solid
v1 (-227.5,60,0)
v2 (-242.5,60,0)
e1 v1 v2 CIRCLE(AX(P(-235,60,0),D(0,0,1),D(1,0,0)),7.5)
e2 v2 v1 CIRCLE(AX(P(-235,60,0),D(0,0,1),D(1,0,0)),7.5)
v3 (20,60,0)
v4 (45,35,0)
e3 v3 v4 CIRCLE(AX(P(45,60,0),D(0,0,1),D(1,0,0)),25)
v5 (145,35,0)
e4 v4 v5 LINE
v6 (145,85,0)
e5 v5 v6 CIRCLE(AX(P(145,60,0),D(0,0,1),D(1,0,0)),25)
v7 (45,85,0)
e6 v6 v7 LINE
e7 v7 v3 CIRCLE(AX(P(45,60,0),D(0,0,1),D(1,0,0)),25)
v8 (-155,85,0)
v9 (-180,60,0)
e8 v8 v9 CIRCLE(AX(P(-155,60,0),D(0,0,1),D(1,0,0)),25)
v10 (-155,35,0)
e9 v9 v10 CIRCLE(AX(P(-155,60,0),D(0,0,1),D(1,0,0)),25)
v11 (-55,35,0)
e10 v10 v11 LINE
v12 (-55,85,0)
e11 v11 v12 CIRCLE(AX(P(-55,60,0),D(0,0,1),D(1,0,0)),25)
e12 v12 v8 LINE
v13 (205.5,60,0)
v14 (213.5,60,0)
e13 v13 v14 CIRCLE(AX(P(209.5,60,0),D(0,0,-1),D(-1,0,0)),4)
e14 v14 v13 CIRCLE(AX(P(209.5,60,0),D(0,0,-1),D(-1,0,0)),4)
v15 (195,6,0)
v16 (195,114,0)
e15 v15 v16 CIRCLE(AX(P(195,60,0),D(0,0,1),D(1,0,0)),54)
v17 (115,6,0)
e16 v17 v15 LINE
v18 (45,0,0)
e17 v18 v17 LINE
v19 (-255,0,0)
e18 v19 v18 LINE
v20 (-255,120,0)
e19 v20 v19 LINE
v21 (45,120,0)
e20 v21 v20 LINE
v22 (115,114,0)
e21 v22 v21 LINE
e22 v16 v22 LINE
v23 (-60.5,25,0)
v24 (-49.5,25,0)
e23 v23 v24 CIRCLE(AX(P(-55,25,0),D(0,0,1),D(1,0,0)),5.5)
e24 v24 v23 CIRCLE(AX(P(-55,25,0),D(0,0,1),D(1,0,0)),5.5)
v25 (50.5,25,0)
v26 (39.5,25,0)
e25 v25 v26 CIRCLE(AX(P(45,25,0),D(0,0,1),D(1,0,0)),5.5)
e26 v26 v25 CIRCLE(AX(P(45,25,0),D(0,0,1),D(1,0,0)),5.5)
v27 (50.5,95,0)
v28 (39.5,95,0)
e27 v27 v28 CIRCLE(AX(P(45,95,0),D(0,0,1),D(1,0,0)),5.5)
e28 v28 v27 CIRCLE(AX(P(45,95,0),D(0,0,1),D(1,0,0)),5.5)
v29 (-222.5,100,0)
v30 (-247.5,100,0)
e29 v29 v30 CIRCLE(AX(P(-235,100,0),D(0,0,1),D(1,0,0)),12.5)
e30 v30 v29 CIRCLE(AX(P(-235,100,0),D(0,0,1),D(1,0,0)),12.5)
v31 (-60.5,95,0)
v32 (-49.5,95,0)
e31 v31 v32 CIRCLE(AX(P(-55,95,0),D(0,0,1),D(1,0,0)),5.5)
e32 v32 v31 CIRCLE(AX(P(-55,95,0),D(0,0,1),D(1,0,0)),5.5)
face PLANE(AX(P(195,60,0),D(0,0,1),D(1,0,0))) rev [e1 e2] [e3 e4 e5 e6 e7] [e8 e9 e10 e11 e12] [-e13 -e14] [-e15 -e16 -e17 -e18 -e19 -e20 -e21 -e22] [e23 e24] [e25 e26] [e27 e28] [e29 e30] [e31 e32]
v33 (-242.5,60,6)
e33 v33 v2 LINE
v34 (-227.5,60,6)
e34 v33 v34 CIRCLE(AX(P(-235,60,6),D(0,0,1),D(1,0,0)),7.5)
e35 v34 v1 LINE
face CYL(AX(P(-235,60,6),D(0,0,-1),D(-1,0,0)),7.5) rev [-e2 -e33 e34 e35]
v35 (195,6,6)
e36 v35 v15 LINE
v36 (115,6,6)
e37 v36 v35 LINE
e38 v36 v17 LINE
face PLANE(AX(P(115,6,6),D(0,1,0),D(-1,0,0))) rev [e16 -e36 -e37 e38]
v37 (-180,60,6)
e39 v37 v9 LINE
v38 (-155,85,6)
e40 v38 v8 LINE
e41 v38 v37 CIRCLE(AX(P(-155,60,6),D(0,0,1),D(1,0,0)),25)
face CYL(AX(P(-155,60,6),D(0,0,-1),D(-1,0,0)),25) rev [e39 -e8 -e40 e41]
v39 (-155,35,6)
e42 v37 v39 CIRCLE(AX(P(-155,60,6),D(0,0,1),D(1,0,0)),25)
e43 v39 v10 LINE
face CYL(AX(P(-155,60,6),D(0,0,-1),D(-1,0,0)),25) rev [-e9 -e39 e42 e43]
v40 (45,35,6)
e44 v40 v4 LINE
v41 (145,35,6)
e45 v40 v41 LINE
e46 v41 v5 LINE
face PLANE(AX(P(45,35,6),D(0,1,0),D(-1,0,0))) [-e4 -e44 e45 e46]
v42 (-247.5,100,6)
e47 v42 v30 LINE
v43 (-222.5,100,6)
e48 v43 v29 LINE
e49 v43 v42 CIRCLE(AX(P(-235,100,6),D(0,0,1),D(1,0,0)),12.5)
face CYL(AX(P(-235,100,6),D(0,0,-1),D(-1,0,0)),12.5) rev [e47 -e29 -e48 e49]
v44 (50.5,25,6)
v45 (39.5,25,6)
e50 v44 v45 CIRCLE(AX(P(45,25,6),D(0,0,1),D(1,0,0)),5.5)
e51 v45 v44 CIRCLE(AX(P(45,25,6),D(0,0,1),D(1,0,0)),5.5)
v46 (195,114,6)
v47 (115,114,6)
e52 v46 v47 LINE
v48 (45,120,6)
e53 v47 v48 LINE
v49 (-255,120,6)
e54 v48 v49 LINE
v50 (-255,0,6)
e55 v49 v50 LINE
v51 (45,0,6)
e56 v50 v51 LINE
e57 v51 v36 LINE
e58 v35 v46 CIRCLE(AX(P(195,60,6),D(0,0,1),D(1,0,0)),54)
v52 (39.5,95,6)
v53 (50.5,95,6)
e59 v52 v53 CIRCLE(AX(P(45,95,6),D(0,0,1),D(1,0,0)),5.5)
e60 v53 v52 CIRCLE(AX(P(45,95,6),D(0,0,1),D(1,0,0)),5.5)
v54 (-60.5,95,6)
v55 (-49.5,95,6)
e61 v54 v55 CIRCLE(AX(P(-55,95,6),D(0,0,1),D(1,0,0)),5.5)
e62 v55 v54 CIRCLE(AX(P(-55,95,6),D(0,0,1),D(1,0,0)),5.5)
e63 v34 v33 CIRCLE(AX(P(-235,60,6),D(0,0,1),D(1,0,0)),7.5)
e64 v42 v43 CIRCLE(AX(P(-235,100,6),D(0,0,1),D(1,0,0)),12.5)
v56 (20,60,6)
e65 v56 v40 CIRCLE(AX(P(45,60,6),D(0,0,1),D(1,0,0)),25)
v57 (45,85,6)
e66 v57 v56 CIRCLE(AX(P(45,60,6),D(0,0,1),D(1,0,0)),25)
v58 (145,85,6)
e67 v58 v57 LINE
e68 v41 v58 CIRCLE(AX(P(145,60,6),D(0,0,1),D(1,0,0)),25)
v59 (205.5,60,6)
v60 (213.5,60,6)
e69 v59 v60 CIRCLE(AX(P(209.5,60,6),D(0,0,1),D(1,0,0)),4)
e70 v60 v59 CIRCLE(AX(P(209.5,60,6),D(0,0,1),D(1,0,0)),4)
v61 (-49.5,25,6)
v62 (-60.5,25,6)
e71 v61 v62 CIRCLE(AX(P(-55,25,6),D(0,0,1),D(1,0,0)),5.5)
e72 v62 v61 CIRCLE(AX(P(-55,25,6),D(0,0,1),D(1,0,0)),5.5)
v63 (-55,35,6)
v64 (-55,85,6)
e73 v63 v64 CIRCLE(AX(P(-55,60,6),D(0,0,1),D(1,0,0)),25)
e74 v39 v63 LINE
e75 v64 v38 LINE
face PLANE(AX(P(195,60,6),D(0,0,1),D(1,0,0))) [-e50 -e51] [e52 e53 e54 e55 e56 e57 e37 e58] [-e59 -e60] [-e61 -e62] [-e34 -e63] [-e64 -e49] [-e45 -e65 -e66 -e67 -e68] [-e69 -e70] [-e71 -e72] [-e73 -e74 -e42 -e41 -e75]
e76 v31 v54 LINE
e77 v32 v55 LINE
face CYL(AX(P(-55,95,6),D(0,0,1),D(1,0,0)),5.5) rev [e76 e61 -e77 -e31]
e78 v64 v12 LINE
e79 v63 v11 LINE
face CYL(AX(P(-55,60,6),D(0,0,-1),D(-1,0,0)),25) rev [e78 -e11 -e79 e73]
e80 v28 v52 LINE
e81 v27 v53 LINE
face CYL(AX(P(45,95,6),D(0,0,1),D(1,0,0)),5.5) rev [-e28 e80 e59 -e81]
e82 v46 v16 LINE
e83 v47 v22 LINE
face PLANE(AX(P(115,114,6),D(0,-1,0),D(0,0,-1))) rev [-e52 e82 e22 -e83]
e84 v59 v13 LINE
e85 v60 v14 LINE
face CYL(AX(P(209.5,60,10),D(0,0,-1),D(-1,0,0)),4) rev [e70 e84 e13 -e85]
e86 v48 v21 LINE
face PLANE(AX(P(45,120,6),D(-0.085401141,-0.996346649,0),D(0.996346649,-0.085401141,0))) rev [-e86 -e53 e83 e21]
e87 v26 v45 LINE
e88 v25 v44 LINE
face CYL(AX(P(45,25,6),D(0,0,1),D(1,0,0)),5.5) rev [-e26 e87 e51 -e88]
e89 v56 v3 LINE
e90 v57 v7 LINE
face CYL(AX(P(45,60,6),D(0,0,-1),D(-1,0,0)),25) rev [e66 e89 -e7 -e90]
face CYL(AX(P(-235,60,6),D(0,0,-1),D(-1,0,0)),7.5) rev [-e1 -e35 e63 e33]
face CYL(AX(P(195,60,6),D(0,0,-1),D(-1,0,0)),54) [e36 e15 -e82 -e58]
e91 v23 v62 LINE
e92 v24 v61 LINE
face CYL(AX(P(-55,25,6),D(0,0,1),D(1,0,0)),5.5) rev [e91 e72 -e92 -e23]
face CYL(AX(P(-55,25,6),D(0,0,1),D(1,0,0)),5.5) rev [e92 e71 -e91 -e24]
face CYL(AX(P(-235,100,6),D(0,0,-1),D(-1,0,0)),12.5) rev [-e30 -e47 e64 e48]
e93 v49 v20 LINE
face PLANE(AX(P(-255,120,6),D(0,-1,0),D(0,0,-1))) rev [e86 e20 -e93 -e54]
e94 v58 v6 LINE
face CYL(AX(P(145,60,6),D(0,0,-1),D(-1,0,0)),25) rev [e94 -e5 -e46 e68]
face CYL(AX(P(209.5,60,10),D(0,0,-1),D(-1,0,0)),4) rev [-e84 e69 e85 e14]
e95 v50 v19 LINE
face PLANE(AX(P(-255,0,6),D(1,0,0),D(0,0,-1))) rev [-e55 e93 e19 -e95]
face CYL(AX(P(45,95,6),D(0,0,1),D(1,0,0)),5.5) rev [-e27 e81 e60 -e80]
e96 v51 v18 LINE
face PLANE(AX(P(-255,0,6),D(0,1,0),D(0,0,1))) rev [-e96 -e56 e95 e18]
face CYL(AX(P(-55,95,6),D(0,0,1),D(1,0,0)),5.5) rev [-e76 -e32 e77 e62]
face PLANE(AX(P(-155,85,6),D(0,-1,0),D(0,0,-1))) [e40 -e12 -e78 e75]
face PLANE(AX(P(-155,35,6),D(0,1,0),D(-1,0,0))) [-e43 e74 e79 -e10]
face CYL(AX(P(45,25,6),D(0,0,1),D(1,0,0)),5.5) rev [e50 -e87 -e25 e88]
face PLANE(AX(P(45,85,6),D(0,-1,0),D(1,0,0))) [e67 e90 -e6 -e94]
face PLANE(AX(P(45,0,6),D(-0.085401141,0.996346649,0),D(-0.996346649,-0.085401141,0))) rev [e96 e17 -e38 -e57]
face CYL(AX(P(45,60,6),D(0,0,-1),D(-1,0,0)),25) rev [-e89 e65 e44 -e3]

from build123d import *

# Parameters (mm, degrees)
SKETCH_1_R                   = 12.5
SKETCH_1_R_2                 = 7.5
EXTRUDE_1_DEPTH              = 6
HOLE_WIZARD_M6_1_D           = 7
HOLE_WIZARD_M6_1_CBORE_D     = 11
HOLE_WIZARD_M6_1_CBORE_DEPTH = 6.8
SKETCH_7_R                   = 4
CUT_EXTRUDE_1_DEPTH          = 10


with BuildPart() as part:
    # 草图1 → 凸台-拉伸1 (new body)
    with BuildSketch(Plane.XY):
        with BuildLine():
            Line((-255, 0), (45, 0))
            Line((45, 0), (115, 6))
            Line((115, 6), (195, 6))
            ThreePointArc((195, 6), (249, 60), (195, 114))
            Line((195, 114), (115, 114))
            Line((115, 114), (45, 120))
            Line((45, 120), (-235, 120))
            Line((-235, 120), (-255, 120))
            Line((-255, 120), (-255, 0))
        make_face()
        with Locations((-235, 100)):
            Circle(SKETCH_1_R, mode=Mode.SUBTRACT)
        with Locations((-235, 60)):
            Circle(SKETCH_1_R_2, mode=Mode.SUBTRACT)
        with BuildLine():
            Line((-155, 85), (-55, 85))
            ThreePointArc((-55, 85), (-30, 60), (-55, 35))
            Line((-55, 35), (-155, 35))
            ThreePointArc((-155, 35), (-180, 60), (-155, 85))
        make_face(mode=Mode.SUBTRACT)
        with BuildLine():
            Line((45, 85), (145, 85))
            ThreePointArc((145, 85), (170, 60), (145, 35))
            Line((145, 35), (45, 35))
            ThreePointArc((45, 35), (20, 60), (45, 85))
        make_face(mode=Mode.SUBTRACT)
    extrude(amount=EXTRUDE_1_DEPTH)

    # M6 六角圆柱头螺钉的柱形沉头孔1 (through all)
    with Locations(Plane.XY.offset(6)):
        with Locations((-55, 95), (-55, 25), (45, 95), (45, 25)):
            CounterBoreHole(HOLE_WIZARD_M6_1_D / 2, HOLE_WIZARD_M6_1_CBORE_D / 2, HOLE_WIZARD_M6_1_CBORE_DEPTH)

    # 草图7 → 切除-拉伸1 (cut)
    with BuildSketch(Plane(origin=(0, 0, 0), x_dir=(-1, 0, 0), z_dir=(0, 0, -1))):
        with Locations((-209.5, 60)):
            Circle(SKETCH_7_R)
    extrude(amount=-CUT_EXTRUDE_1_DEPTH, mode=Mode.SUBTRACT)


solid = part.part
